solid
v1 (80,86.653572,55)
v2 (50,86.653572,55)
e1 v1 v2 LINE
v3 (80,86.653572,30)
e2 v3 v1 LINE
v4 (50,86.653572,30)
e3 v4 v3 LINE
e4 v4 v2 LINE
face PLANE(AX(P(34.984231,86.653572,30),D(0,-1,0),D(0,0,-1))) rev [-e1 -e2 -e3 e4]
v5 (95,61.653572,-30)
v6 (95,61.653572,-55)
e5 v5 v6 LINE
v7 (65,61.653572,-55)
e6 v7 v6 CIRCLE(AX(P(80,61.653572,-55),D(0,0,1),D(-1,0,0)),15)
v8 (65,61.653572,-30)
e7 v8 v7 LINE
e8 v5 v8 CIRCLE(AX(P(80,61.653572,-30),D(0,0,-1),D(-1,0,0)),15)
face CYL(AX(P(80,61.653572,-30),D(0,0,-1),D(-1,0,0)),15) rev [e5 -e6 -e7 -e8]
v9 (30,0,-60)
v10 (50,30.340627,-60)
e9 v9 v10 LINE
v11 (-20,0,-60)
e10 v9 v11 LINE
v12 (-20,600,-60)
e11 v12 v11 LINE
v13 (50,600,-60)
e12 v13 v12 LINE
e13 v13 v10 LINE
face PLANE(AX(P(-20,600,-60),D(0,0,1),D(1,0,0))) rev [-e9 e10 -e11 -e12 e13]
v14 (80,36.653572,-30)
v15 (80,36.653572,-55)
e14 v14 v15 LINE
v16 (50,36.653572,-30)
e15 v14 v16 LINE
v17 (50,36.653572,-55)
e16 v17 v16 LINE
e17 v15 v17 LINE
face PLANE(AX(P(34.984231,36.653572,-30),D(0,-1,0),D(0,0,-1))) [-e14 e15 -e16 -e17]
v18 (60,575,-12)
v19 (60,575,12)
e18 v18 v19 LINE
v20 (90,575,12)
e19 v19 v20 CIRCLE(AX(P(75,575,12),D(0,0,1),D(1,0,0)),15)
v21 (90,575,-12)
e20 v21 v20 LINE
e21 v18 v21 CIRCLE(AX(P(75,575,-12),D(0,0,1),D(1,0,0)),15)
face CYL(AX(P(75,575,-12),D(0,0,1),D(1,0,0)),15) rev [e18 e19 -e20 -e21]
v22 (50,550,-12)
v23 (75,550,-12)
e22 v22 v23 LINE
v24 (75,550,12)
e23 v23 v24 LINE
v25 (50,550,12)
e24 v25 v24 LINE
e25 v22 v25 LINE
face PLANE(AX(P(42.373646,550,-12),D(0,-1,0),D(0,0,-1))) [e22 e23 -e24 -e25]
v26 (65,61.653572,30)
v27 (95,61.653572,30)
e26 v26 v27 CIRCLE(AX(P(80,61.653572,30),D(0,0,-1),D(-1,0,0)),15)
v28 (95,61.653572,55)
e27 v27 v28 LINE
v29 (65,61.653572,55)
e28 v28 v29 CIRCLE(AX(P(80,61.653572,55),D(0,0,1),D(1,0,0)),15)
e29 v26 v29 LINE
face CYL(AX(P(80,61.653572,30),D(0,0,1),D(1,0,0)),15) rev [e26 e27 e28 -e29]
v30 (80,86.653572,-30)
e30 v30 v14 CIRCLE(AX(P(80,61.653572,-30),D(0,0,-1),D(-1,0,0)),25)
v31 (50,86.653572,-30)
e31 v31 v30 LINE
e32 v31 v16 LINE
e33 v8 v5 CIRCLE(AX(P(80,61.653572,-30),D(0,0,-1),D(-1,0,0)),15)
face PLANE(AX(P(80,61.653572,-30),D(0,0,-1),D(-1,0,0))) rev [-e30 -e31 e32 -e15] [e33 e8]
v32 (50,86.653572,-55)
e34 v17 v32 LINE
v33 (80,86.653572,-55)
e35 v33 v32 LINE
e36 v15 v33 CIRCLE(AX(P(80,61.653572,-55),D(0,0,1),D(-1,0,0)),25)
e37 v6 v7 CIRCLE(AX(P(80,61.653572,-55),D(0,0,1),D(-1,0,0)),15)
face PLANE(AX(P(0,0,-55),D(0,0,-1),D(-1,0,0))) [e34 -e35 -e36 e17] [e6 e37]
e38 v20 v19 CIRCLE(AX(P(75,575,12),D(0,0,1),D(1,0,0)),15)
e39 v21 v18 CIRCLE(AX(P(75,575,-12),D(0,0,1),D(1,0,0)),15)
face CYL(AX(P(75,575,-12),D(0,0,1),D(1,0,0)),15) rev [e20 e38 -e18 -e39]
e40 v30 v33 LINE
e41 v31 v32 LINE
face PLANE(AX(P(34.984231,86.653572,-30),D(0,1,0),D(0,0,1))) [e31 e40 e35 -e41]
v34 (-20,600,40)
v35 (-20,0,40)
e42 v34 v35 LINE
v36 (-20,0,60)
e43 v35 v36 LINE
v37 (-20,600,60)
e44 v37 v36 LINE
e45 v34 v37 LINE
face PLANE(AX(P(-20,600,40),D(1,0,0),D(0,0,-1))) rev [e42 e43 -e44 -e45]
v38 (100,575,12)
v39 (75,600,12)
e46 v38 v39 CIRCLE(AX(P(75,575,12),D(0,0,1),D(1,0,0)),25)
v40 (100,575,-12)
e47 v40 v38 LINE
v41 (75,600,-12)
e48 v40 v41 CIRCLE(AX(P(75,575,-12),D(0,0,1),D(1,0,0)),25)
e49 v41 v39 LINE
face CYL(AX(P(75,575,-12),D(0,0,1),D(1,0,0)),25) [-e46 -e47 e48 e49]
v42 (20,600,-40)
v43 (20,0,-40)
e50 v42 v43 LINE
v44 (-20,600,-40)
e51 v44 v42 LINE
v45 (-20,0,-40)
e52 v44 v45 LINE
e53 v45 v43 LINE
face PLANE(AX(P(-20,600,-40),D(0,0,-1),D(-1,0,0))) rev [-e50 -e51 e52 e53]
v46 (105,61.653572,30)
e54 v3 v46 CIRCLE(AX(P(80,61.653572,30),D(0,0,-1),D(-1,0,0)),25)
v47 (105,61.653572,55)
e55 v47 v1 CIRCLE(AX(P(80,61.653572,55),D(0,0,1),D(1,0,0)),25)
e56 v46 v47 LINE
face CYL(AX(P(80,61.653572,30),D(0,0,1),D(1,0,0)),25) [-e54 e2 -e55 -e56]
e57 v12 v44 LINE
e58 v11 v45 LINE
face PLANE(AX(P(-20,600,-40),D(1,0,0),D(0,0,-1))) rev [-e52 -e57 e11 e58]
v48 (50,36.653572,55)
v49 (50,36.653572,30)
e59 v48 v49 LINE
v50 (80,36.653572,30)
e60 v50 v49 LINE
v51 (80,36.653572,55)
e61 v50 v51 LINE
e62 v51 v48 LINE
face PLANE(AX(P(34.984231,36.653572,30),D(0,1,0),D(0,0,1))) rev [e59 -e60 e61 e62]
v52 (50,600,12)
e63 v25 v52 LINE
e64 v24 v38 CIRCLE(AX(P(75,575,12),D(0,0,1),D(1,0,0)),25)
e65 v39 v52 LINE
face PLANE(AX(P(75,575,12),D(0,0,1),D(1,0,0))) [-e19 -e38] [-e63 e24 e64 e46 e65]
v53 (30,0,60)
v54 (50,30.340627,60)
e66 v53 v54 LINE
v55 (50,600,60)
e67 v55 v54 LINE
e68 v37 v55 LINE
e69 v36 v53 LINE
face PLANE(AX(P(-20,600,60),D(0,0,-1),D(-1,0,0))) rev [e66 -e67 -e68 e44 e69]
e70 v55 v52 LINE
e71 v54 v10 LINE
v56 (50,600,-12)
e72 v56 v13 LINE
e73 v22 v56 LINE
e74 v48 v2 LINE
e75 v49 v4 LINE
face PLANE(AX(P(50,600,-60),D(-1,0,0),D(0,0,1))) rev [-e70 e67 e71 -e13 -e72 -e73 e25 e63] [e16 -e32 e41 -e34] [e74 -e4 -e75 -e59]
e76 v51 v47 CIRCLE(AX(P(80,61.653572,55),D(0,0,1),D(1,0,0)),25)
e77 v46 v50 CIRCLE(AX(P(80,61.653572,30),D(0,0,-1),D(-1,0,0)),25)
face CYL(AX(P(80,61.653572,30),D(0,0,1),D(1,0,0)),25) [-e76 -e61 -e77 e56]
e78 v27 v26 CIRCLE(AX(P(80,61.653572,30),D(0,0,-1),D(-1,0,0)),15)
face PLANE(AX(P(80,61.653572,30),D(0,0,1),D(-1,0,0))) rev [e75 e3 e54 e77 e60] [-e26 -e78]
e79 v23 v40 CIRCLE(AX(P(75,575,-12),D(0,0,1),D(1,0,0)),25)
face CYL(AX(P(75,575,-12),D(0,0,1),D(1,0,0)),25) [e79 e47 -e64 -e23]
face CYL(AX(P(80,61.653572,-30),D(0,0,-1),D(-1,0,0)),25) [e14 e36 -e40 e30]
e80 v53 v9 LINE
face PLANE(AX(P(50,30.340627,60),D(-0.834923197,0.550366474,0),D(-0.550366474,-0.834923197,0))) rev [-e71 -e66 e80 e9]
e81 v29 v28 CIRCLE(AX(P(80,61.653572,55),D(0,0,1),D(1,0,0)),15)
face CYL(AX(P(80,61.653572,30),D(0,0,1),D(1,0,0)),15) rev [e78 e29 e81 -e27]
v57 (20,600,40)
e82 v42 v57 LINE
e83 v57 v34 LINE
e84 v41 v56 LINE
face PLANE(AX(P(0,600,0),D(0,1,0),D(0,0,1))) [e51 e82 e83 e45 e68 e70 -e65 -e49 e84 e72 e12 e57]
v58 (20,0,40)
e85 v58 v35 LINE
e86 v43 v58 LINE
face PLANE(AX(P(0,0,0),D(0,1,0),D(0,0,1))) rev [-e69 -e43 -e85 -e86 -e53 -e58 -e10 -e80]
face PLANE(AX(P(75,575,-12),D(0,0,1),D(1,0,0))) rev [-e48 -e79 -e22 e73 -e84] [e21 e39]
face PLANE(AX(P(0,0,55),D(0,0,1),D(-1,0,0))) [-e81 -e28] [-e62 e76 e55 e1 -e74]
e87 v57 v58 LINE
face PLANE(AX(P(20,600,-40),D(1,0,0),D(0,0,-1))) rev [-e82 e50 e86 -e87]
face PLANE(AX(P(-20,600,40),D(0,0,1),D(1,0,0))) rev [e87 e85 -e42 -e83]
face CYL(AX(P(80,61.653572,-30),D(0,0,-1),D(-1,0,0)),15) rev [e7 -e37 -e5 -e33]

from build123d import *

# Parameters (mm, degrees)
BOSS_EXTRUDE1_DEPTH      = 600
SKETCH2_R                = 15
BOSS_EXTRUDE2_DEPTH      = 30
BOSS_EXTRUDE3_DEPTH      = 12
BOSS_EXTRUDE3_DEPTH_BACK = 12
SKETCH3_R                = 15
SKETCH4_W                = 64.999273694
SKETCH4_H                = 54.968001075
CUT_EXTRUDE1_DEPTH       = 5
CUT_EXTRUDE2_DEPTH       = 621.826062597


with BuildPart() as part:
    # Sketch1 → Boss-Extrude1 (new body)
    with BuildSketch(Plane(origin=(0, 0, 0), x_dir=(1, 0, 0), z_dir=(0, 1, 0))):
        Polygon((-20, 40), (-20, 60), (50, 60), (50, -60), (-20, -60), (-20, -40), (20, -40), (20, 40), align=None)
    extrude(amount=BOSS_EXTRUDE1_DEPTH)

    # Sketch2 → Boss-Extrude2 (add)
    with BuildSketch(Plane(origin=(0, 0, -60), x_dir=(-1, 0, 0), z_dir=(0, 0, -1))):
        with BuildLine():
            Line((-34.984231122, 36.653571932), (-80, 36.653571932))
            ThreePointArc((-80, 36.653571932), (-105, 61.653571932), (-80, 86.653571932))
            Line((-80, 86.653571932), (-34.984231122, 86.653571932))
            Line((-34.984231122, 86.653571932), (-34.984231122, 36.653571932))
        make_face()
        with Locations((-80, 61.653571932)):
            Circle(SKETCH2_R, mode=Mode.SUBTRACT)
    boss_extrude2 = extrude(amount=-BOSS_EXTRUDE2_DEPTH)

    # Mirror1: Boss-Extrude2 across plane
    add(boss_extrude2.mirror(Plane.XY))

    # Sketch3 → Boss-Extrude3 (add, two sides: drawn at the far end of the back side and taken through both)
    with BuildSketch(Plane.XY.offset(-BOSS_EXTRUDE3_DEPTH_BACK)):
        with BuildLine():
            Line((42.373646318, 600), (75, 600))
            ThreePointArc((75, 600), (100, 575), (75, 550))
            Line((75, 550), (42.373646318, 550))
            Line((42.373646318, 550), (42.373646318, 600))
        make_face()
        with Locations((75, 575)):
            Circle(SKETCH3_R, mode=Mode.SUBTRACT)
    extrude(amount=BOSS_EXTRUDE3_DEPTH + BOSS_EXTRUDE3_DEPTH_BACK)

    # Sketch4 → Cut-Extrude1 (cut)
    with BuildSketch(Plane(origin=(0, 0, -60), x_dir=(-1, 0, 0), z_dir=(0, 0, -1))):
        with Locations((-82.499636847, 64.13757247)):
            Rectangle(SKETCH4_W, SKETCH4_H)
    cut_extrude1 = extrude(amount=-CUT_EXTRUDE1_DEPTH, mode=Mode.SUBTRACT)

    # Mirror2: Cut-Extrude1 across plane
    add(cut_extrude1.mirror(Plane.XY), mode=Mode.SUBTRACT)

    # Sketch5 → Cut-Extrude2 (cut, through all)
    with BuildSketch(Plane(origin=(0, 0, -60), x_dir=(-1, 0, 0), z_dir=(0, 0, -1))):
        Polygon((-50, 30.340627067), (-30, 0), (-50, 0), align=None)
    extrude(amount=-CUT_EXTRUDE2_DEPTH, mode=Mode.SUBTRACT)


solid = part.part
